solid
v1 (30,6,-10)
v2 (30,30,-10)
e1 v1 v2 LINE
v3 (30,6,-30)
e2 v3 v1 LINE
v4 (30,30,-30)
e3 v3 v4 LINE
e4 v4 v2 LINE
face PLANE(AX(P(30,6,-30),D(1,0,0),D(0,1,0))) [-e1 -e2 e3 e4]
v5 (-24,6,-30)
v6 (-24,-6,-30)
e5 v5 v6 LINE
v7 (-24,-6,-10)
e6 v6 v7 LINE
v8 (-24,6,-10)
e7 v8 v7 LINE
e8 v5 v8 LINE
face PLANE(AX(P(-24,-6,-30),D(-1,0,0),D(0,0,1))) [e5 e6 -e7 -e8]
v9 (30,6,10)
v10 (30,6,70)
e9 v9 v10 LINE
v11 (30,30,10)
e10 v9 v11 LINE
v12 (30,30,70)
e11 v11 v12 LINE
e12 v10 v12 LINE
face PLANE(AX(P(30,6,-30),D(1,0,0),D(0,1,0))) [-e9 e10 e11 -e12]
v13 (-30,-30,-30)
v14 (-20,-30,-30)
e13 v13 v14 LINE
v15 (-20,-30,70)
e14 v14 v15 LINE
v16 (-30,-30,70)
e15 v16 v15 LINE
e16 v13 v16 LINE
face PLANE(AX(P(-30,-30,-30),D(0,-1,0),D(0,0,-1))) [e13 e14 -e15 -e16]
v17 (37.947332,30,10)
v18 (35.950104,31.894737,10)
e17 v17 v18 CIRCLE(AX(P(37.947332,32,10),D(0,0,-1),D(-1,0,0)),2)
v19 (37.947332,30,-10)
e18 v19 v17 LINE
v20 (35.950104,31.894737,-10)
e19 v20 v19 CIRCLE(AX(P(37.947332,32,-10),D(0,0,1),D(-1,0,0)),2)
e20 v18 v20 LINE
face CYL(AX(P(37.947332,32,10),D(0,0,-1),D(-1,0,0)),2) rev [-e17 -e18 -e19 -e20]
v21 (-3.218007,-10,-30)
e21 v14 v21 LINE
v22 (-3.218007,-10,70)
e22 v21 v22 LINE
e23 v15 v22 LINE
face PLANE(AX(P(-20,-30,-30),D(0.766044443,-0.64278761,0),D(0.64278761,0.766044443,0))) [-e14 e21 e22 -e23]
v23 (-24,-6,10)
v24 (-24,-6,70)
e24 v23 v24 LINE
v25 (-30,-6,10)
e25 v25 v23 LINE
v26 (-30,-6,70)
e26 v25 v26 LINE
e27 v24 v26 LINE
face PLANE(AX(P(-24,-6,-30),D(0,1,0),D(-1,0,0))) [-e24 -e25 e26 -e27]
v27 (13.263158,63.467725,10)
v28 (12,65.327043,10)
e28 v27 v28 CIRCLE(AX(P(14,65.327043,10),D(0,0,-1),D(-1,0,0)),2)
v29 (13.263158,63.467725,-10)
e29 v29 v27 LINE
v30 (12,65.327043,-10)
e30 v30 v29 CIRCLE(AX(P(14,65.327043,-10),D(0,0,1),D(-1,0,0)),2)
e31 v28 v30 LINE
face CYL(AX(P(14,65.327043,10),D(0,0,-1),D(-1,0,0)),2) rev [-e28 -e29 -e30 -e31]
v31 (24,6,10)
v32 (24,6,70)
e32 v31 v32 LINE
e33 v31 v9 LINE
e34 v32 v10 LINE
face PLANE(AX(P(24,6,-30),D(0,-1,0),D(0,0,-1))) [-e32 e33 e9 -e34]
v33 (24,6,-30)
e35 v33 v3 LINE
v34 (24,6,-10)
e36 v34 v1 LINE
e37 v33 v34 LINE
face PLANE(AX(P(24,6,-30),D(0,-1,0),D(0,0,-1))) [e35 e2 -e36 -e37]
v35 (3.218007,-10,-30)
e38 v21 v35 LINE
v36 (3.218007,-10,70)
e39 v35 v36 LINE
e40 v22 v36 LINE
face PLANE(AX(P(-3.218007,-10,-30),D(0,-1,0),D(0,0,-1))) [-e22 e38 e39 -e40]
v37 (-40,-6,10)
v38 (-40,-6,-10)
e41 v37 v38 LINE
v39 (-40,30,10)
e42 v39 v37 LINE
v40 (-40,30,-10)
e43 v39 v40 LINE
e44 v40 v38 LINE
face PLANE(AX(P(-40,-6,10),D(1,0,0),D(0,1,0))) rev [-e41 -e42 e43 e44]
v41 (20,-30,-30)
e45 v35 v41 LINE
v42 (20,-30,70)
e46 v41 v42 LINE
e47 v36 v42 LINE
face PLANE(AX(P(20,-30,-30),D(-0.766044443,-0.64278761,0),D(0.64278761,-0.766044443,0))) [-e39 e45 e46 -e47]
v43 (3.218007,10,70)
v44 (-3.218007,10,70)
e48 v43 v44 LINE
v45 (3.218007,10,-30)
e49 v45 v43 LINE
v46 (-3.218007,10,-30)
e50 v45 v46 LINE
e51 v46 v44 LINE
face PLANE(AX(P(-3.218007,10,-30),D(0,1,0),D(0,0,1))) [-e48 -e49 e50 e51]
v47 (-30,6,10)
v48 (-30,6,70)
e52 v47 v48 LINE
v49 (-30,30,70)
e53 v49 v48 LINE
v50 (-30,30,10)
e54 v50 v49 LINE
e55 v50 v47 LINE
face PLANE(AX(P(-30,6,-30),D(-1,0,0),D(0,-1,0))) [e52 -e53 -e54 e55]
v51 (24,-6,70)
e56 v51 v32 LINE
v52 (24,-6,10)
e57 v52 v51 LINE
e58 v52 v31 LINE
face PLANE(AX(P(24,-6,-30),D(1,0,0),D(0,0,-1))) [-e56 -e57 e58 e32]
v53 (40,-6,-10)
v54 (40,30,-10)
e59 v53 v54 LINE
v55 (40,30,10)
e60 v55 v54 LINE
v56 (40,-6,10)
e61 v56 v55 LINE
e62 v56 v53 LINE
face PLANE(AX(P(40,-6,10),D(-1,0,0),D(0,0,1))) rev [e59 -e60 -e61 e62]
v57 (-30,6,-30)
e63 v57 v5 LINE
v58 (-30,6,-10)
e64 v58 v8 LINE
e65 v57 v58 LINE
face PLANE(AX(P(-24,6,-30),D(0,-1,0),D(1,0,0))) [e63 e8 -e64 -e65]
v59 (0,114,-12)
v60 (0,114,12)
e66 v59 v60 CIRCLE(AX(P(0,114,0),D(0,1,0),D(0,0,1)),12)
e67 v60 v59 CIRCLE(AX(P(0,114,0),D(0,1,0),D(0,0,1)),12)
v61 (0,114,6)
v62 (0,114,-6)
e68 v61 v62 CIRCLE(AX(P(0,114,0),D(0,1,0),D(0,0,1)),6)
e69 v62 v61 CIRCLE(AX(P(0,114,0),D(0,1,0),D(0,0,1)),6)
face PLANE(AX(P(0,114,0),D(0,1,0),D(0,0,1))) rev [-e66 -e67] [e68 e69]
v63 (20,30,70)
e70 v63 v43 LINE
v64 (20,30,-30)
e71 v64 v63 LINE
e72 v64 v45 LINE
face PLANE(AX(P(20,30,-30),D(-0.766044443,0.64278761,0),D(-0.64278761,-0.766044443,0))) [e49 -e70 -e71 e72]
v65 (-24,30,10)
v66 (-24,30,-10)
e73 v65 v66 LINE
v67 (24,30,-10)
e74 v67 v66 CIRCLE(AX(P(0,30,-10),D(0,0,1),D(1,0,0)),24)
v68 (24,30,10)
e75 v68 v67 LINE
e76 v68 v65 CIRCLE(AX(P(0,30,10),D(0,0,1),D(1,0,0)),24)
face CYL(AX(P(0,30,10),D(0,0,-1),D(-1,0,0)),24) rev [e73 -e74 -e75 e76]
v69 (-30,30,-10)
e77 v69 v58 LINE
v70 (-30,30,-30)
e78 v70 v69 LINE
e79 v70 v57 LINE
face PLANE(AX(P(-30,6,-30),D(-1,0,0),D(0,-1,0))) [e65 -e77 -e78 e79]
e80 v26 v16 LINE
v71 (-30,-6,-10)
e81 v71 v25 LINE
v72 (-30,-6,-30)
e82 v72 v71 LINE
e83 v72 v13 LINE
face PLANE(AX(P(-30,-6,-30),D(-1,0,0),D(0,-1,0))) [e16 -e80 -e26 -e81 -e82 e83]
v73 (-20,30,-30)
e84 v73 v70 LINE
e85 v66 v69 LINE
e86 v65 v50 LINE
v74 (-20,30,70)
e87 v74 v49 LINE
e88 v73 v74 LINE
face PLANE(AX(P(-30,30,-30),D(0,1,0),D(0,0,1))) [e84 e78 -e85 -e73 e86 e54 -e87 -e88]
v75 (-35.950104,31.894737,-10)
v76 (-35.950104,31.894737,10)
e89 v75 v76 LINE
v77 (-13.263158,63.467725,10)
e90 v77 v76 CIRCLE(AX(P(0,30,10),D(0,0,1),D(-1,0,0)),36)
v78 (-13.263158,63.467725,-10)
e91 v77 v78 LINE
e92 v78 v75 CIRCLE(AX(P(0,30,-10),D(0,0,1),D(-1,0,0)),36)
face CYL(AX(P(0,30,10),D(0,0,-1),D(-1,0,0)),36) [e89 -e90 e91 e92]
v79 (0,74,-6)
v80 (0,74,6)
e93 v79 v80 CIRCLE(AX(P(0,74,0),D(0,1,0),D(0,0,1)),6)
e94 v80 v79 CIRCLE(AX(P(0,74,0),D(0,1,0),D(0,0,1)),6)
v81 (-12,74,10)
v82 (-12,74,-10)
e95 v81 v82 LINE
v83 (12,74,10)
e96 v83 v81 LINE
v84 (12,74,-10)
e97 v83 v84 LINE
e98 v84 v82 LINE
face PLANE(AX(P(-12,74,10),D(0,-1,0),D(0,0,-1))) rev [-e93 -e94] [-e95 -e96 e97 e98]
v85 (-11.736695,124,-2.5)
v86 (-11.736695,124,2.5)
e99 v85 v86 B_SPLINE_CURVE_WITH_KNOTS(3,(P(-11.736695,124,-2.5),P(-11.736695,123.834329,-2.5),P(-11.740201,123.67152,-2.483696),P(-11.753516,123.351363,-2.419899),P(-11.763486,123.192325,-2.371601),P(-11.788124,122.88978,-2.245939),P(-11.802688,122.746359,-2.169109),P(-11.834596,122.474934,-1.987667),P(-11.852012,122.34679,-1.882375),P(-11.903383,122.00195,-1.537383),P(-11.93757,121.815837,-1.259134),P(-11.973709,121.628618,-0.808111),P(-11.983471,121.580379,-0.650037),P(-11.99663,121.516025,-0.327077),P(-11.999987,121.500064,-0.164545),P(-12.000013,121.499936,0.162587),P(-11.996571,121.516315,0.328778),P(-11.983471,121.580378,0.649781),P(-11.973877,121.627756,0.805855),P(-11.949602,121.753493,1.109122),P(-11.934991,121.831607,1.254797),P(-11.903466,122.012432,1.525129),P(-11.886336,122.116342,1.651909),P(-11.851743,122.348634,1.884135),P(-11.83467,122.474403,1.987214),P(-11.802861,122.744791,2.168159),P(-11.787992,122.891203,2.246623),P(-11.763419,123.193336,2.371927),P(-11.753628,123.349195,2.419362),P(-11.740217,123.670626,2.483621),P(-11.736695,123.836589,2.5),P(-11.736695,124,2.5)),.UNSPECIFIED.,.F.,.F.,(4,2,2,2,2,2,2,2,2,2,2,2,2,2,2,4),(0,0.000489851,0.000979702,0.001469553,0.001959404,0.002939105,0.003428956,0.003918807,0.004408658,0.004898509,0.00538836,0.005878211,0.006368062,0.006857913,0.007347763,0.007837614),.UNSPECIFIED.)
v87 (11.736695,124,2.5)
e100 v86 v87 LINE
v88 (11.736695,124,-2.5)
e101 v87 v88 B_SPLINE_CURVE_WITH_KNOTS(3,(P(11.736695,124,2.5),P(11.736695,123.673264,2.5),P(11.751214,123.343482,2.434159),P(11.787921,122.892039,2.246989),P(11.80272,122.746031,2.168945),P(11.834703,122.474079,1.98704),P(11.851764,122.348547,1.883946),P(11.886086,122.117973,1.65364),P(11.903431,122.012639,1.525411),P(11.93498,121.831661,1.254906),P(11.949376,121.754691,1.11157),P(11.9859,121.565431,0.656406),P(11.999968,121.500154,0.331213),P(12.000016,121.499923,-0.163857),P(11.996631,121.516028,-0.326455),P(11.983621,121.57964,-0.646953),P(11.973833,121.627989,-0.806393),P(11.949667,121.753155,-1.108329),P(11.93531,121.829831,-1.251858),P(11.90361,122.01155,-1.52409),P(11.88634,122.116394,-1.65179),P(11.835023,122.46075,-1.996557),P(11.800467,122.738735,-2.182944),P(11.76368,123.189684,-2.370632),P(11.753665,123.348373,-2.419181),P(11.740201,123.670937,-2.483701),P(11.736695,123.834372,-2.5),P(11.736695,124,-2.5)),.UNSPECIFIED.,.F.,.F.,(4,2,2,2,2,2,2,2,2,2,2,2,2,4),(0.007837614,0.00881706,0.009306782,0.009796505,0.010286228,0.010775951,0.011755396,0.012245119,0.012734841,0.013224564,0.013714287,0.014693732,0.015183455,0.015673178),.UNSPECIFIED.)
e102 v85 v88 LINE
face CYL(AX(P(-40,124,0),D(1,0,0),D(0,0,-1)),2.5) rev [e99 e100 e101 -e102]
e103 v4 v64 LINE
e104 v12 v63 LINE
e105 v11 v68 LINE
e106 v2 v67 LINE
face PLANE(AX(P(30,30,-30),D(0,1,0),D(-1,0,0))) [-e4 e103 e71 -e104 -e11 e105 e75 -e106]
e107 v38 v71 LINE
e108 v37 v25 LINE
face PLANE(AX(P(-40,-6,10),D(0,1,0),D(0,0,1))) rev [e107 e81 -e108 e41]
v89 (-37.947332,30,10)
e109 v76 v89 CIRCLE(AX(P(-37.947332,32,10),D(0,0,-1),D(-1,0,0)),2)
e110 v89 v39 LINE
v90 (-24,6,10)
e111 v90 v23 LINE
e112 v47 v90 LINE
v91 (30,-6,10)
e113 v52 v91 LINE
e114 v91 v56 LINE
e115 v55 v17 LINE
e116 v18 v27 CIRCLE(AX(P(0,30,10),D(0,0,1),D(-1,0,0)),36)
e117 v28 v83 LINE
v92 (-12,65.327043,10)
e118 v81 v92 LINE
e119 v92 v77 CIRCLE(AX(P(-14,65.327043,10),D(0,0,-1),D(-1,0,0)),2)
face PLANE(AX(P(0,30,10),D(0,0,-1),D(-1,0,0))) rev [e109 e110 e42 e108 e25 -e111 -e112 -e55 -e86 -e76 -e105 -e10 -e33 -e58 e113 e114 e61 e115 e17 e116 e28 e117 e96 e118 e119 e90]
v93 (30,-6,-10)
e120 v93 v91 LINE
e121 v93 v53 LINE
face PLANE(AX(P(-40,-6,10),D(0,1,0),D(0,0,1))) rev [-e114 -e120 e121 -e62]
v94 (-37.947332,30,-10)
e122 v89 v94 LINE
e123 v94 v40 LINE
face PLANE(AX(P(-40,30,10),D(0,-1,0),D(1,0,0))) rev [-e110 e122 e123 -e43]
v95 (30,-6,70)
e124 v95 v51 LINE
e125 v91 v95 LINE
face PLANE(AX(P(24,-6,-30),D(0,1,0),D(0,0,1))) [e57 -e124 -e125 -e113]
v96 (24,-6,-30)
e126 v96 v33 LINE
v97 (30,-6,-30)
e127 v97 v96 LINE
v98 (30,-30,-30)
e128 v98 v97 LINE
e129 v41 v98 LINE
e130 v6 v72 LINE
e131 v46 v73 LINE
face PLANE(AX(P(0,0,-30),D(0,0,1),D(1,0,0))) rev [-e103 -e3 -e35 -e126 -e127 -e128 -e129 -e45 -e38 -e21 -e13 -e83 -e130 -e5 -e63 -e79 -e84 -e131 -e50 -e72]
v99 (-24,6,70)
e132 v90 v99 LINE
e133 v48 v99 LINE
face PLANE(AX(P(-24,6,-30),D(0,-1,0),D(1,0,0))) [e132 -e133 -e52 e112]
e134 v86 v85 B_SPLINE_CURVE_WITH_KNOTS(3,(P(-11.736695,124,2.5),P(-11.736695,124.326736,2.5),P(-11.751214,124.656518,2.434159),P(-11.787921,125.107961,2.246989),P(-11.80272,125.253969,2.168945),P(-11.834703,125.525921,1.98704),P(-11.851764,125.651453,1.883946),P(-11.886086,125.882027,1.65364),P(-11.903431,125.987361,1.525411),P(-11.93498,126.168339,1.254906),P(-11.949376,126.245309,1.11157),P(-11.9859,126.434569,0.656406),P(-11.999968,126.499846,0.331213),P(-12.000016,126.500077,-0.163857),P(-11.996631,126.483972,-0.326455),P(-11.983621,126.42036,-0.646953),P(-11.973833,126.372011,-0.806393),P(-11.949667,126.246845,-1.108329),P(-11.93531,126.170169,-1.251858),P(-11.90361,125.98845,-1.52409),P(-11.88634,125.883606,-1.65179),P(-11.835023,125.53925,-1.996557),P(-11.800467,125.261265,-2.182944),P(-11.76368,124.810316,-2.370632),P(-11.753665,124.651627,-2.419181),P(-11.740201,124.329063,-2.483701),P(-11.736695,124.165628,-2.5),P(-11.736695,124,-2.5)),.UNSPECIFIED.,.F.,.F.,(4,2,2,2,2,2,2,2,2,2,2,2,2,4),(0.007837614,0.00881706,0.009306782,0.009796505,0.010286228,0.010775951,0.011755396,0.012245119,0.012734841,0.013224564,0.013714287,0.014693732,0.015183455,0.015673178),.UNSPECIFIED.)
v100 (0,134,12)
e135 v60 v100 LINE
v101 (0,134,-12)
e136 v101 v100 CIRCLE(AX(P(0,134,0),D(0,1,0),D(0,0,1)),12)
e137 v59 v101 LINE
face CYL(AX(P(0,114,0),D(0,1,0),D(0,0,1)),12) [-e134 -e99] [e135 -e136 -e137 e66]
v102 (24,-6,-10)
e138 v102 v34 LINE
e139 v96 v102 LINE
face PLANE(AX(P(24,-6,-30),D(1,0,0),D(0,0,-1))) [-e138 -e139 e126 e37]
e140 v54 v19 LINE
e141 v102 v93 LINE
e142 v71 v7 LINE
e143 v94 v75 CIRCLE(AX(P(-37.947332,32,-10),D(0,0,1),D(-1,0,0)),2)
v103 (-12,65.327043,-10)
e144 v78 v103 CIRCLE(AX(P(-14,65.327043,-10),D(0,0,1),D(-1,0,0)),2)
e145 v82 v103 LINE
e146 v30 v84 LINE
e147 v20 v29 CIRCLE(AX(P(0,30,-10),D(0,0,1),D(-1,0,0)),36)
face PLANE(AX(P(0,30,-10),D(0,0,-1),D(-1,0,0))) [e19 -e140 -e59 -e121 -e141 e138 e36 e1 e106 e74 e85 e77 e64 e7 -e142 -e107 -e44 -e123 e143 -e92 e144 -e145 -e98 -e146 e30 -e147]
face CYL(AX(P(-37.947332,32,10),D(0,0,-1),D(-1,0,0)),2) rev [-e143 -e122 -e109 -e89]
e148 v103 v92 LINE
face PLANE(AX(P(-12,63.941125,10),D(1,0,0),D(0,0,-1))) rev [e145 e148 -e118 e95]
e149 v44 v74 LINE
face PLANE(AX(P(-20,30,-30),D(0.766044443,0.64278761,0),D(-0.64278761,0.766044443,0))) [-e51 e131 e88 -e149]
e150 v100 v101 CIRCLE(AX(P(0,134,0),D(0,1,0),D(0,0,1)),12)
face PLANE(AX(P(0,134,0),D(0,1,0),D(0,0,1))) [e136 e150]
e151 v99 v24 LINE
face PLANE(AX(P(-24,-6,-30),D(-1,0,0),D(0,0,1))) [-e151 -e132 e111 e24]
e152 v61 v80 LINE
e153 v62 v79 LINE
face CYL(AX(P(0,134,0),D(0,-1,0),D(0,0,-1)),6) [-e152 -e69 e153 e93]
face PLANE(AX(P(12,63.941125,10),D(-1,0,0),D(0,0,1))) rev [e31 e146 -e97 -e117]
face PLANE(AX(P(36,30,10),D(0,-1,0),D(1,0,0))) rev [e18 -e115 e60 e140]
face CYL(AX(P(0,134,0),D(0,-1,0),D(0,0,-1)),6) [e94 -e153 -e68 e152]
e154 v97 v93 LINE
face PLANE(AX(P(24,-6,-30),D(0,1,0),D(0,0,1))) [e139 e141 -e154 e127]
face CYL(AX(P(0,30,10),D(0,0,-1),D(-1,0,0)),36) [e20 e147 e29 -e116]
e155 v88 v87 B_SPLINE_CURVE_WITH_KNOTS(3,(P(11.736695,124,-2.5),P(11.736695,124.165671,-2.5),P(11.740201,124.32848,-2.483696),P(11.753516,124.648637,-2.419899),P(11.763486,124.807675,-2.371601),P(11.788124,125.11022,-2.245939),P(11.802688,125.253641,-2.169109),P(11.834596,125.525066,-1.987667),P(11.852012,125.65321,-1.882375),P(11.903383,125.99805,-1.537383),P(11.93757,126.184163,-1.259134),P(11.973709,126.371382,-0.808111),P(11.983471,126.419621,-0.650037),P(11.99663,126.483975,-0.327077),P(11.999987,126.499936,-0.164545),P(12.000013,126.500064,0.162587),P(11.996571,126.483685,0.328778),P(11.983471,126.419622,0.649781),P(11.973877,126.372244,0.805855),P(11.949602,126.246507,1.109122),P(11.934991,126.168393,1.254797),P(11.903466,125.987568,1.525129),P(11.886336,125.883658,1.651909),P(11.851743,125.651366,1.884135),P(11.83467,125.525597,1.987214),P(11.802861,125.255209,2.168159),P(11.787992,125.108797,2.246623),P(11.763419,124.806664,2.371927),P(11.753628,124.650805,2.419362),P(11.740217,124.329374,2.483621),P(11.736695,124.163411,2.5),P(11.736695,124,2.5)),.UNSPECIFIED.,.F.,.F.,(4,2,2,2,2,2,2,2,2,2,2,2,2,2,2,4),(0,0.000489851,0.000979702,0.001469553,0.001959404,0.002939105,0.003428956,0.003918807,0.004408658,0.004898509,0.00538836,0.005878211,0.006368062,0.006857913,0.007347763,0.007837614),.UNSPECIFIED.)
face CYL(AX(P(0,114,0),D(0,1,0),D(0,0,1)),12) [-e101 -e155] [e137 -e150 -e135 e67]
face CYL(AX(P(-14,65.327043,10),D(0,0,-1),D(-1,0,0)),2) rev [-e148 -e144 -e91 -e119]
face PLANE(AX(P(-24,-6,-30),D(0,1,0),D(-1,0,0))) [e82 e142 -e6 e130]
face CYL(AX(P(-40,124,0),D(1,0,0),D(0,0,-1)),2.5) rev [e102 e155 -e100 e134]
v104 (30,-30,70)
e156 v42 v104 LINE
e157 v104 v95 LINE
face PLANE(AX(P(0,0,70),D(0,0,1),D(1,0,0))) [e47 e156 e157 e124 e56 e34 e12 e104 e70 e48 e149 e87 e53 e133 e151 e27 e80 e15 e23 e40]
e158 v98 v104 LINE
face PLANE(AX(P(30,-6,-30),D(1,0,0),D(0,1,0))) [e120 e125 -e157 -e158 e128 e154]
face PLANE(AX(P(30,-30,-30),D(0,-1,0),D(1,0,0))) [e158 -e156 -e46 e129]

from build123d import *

# Parameters (mm, degrees)
V_BLOCK_BASE_DEPTH         = 70
V_BLOCK_BASE_DEPTH_BACK    = 30
CLAMP_ARCH_DEPTH           = 10
CLAMP_ARCH_FILLET_R2_R     = 2
CLAMP_SCREW_SKETCH_R       = 6
CLAMP_SCREW_SHAFT_DEPTH    = 60
CLAMP_START                = 40
SKETCH4_3_R                = 12
SKETCH4_3_R_2              = 6
CLAMP_SCREW_KNOB_DEPTH     = 20
KNOB_CROSS_HOLE_DEPTH      = 157.384142419
KNOB_CROSS_HOLE_DEPTH_BACK = 157.384142419
KNOB_CROSS_HOLE_SKETCH_R   = 2.5


with BuildPart() as part:
    # V-Block Profile Sketch → V-Block Base (new, two sides: drawn at the far end of the back side and taken through both)
    with BuildSketch(Plane.XY.offset(-V_BLOCK_BASE_DEPTH_BACK)):
        Polygon((-24, -6), (-30, -6), (-30, -30), (-20, -30), (-3.218007376, -10), (3.218007376, -10), (20, -30), (30, -30), (30, -6), (24, -6), (24, 6), (30, 6), (30, 30), (20, 30), (3.218007376, 10), (-3.218007376, 10), (-20, 30), (-30, 30), (-30, 6), (-24, 6), align=None)
    extrude(amount=V_BLOCK_BASE_DEPTH + V_BLOCK_BASE_DEPTH_BACK)

    # Clamp Arch Sketch → Clamp Arch (add, symmetric)
    with BuildSketch(Plane.XY):
        with BuildLine():
            Line((-40, -6), (40, -6))
            Line((40, -6), (40, 30))
            Line((40, 30), (36, 30))
            ThreePointArc((36, 30), (29.393876913, 50.784609691), (12, 63.941125497))
            Line((12, 63.941125497), (12, 74))
            Line((12, 74), (-12, 74))
            Line((-12, 74), (-12, 63.941125497))
            ThreePointArc((-12, 63.941125497), (-29.393876913, 50.784609691), (-36, 30))
            Line((-36, 30), (-40, 30))
            Line((-40, 30), (-40, -6))
        make_face()
        with BuildLine():
            Line((-20, 30), (-24, 30))
            ThreePointArc((-24, 30), (0, 54), (24, 30))
            Line((24, 30), (20, 30))
            Line((20, 30), (3.218007376, 10))
            Line((3.218007376, 10), (-3.218007376, 10))
            Line((-3.218007376, 10), (-20, 30))
        make_face(mode=Mode.SUBTRACT)
    extrude(amount=CLAMP_ARCH_DEPTH, both=True)

    # Clamp Arch Fillet R2
    clamp_arch_fillet_r2_edges = [part.edges().sort_by_distance(p)[0] for p in [
        (36, 30, 0),
        (12, 63.941125497, 0),
        (-12, 63.941125497, 0),
        (-36, 30, 0),
    ]]
    fillet(clamp_arch_fillet_r2_edges, radius=CLAMP_ARCH_FILLET_R2_R)

    # Clamp Screw Sketch → Clamp Screw Shaft (add)
    with BuildSketch(Plane(origin=(0, 74, 0), x_dir=(1, 0, 0), z_dir=(0, 1, 0))):
        with Locations(Location((0, 0, 0), (0, 0, 270))):
            Circle(CLAMP_SCREW_SKETCH_R)
    extrude(amount=CLAMP_SCREW_SHAFT_DEPTH)

    # Sketch4_3 → Clamp Screw Knob (add)
    with BuildSketch(Plane(origin=(0, 74, 0), x_dir=(1, 0, 0), z_dir=(0, 1, 0)).offset(CLAMP_START)):
        with Locations(Location((0, 0, 0), (0, 0, 270))):
            Circle(SKETCH4_3_R)
        with Locations(Location((0, 0, 0), (0, 0, 270))):
            Circle(SKETCH4_3_R_2, mode=Mode.SUBTRACT)
    extrude(amount=CLAMP_SCREW_KNOB_DEPTH)

    # Knob Cross Hole Sketch → Knob Cross Hole (cut, two sides: drawn at the far end of the back side and taken through both)
    with BuildSketch(Plane(origin=(0, 0, 0), x_dir=(0, 0, -1), z_dir=(1, 0, 0)).offset(-KNOB_CROSS_HOLE_DEPTH_BACK)):
        with Locations((0, 124)):
            Circle(KNOB_CROSS_HOLE_SKETCH_R)
    extrude(amount=KNOB_CROSS_HOLE_DEPTH + KNOB_CROSS_HOLE_DEPTH_BACK, mode=Mode.SUBTRACT)


solid = part.part
